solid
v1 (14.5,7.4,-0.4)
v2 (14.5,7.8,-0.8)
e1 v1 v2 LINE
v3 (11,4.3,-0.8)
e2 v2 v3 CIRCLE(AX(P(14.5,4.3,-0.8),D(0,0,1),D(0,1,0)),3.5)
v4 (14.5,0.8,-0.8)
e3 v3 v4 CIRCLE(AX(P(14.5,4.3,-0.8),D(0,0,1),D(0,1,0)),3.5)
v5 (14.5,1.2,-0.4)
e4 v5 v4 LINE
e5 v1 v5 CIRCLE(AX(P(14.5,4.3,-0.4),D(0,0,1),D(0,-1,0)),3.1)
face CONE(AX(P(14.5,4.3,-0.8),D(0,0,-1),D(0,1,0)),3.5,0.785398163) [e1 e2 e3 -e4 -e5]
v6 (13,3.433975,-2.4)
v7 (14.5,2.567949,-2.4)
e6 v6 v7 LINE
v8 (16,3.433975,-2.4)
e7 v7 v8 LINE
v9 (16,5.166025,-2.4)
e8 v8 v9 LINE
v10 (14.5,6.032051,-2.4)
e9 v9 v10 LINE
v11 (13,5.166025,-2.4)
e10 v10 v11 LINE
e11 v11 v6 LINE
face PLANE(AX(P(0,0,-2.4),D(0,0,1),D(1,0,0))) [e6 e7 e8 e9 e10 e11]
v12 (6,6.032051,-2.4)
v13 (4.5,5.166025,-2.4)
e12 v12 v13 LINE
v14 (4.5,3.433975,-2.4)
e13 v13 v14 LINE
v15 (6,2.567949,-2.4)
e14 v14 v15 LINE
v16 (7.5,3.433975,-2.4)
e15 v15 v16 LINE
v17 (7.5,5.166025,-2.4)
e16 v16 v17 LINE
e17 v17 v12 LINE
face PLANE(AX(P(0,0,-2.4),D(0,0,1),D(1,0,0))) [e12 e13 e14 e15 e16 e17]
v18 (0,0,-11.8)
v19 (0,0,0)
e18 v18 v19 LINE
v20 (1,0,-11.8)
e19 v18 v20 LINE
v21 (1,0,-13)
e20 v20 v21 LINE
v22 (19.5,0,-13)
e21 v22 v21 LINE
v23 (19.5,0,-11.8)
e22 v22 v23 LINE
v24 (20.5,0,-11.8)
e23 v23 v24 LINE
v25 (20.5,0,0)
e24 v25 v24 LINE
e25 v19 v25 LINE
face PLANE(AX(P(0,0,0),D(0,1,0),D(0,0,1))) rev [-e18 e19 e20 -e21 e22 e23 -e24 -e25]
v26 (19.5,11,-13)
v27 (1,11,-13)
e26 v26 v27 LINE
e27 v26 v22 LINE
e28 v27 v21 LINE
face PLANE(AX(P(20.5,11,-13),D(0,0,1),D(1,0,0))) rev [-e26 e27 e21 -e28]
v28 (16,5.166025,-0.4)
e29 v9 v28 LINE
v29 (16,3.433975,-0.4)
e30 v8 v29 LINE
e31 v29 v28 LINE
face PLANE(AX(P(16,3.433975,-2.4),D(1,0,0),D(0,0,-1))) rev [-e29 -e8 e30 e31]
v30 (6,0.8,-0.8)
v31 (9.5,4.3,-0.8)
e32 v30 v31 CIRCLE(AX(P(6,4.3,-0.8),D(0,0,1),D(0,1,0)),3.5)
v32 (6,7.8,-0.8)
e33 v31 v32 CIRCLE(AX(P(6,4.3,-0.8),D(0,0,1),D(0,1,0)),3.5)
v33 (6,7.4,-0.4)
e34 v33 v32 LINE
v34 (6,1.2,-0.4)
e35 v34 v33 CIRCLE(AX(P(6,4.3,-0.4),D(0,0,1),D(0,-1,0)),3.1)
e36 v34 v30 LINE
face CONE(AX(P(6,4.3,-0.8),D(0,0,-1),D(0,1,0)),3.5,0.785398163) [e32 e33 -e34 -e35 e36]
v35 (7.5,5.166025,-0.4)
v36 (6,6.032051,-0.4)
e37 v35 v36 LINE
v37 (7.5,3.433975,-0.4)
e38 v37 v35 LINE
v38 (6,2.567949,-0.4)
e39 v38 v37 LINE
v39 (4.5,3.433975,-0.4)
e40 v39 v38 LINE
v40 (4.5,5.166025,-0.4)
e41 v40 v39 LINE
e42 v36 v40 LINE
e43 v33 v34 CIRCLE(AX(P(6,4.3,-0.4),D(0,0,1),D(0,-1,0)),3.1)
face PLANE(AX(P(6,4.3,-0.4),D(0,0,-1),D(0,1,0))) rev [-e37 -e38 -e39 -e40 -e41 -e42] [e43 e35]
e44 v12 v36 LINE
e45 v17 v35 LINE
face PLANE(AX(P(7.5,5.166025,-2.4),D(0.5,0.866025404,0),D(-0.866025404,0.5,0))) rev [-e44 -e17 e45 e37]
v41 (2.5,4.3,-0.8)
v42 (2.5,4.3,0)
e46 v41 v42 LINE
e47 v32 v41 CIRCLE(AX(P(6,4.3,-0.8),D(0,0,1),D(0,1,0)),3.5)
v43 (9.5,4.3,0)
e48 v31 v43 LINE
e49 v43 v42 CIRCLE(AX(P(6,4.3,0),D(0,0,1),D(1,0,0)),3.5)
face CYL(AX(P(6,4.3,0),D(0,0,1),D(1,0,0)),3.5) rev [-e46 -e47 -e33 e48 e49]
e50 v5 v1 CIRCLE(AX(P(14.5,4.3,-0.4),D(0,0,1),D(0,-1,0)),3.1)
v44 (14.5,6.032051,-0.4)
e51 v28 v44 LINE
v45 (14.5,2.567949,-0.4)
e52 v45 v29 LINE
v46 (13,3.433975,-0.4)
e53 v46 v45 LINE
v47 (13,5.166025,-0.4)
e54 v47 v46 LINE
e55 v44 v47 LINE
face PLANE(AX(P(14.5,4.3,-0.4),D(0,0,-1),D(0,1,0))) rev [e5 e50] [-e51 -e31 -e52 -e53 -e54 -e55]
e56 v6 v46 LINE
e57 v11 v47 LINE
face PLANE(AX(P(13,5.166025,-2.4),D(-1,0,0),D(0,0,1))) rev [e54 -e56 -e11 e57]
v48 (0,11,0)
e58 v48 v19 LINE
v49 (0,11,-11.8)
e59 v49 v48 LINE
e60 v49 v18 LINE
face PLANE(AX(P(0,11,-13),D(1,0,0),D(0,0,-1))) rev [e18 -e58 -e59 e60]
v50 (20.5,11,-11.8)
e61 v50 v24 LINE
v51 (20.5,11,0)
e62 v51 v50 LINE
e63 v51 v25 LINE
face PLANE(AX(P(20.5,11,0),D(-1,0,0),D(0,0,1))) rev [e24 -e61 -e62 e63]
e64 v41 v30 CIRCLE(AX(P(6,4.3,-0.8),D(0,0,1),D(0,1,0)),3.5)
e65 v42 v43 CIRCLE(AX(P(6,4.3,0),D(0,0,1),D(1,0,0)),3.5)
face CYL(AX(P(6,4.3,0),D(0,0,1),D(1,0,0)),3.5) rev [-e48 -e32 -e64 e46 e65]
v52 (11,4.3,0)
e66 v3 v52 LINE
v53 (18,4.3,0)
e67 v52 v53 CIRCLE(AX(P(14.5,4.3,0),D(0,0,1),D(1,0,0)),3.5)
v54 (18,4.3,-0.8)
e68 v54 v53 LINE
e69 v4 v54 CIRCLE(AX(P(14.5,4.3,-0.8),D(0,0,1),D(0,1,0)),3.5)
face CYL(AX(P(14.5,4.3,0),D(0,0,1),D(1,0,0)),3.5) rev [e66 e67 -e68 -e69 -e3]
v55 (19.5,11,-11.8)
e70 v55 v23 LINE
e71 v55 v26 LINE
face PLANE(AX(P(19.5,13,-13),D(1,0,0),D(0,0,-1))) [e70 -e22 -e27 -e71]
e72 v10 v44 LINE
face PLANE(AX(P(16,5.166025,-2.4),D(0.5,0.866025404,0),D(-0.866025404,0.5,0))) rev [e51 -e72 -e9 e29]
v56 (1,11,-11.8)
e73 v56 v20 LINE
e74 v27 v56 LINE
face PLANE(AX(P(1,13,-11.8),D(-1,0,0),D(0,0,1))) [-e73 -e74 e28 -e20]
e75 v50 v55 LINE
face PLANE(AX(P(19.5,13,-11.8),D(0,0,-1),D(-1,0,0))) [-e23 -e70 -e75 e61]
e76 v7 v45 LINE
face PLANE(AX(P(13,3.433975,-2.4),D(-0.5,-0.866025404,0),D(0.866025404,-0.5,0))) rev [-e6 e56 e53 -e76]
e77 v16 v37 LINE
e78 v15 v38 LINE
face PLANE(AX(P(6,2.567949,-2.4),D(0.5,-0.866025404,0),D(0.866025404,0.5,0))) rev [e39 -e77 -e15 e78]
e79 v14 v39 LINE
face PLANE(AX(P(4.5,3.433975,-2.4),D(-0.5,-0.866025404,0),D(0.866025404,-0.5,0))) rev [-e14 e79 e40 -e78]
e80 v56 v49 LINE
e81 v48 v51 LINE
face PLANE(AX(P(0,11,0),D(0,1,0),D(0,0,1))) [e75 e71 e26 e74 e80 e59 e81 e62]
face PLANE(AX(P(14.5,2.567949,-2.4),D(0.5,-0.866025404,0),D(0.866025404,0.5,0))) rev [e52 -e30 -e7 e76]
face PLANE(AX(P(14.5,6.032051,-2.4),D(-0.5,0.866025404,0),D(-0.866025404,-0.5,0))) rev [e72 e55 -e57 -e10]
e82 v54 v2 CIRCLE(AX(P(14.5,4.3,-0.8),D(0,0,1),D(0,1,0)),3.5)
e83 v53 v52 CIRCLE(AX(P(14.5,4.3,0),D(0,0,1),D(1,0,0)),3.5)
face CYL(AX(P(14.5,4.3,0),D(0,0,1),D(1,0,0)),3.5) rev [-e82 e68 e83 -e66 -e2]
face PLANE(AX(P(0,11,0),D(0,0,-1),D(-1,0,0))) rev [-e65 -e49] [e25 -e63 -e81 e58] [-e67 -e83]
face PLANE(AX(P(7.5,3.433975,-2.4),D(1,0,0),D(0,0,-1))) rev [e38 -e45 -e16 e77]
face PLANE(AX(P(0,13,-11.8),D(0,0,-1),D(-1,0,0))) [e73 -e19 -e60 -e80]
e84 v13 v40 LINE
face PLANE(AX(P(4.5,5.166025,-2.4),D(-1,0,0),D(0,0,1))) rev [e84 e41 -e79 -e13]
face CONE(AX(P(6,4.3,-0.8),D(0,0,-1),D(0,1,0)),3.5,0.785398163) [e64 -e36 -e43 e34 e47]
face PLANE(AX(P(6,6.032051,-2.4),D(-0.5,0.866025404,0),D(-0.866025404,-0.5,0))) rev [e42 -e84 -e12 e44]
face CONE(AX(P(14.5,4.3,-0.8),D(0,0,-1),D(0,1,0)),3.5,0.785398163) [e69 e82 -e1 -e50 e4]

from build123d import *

# Parameters (mm, degrees)
SKETCH_1_W          = 20.5
SKETCH_1_H          = 13
EXTRUDE_1_DEPTH     = 11
CUT_EXTRUDE_1_DEPTH = 13
HOLE_WIZARD_1_D     = 7
HOLE_WIZARD_1_DEPTH = 4.4
HOLE_WIZARD_2_D     = 7
HOLE_WIZARD_2_DEPTH = 4.4
CUT_EXTRUDE_2_DEPTH = 2
CUT_EXTRUDE_3_DEPTH = 2


with BuildPart() as part:
    # 草图1 → 凸台-拉伸1 (new body)
    with BuildSketch(Plane(origin=(0, 0, 0), x_dir=(1, 0, 0), z_dir=(0, 1, 0))):
        with Locations((10.25, 6.5)):
            Rectangle(SKETCH_1_W, SKETCH_1_H)
    extrude(amount=EXTRUDE_1_DEPTH)

    # 草图2 → 切除-拉伸1 (cut)
    with BuildSketch(Plane(origin=(0, 0, 0), x_dir=(1, 0, 0), z_dir=(0, 1, 0))):
        Polygon((0, 11.8), (1, 11.8), (1, 13), (19.5, 13), (19.5, 11.8), (20.5, 11.8), (20.5, 26), (0, 26), align=None)
    extrude(amount=CUT_EXTRUDE_1_DEPTH, mode=Mode.SUBTRACT)

    # 孔1
    with Locations(Plane.XY):
        with Locations((6, 4.3)):
            Hole(HOLE_WIZARD_1_D / 2, depth=HOLE_WIZARD_1_DEPTH)

    # 孔2
    with Locations(Plane.XY):
        with Locations((14.5, 4.3)):
            Hole(HOLE_WIZARD_2_D / 2, depth=HOLE_WIZARD_2_DEPTH)

    # 草图7 → 旋转1 (revolve)
    with BuildSketch(Plane(origin=(6, 0, 0), x_dir=(0, 0, -1), z_dir=(1, 0, 0)), mode=Mode.PRIVATE) as revolve_1_sk:
        Polygon((0.4, 4.3), (0.4, 7.4), (0.8, 7.8), (4.4, 7.8), (4.4, 4.3), align=None)
    revolve(revolve_1_sk.sketch.rotate(Axis((6, 4.3, -4.4), (0, 0, 1)), 270), axis=Axis((6, 4.3, -4.4), (0, 0, 1)))

    # 草图8 → 旋转2 (revolve)
    with BuildSketch(Plane(origin=(14.5, 0, 0), x_dir=(0, 0, -1), z_dir=(1, 0, 0)), mode=Mode.PRIVATE) as revolve_2_sk:
        Polygon((0.4, 4.3), (0.4, 7.4), (0.8, 7.8), (4.4, 7.8), (4.4, 4.3), align=None)
    revolve(revolve_2_sk.sketch.rotate(Axis((14.5, 4.3, -4.4), (0, 0, 1)), 270), axis=Axis((14.5, 4.3, -4.4), (0, 0, 1)))

    # 草图9 → 切除-拉伸2 (cut)
    with BuildSketch(Plane.XY.offset(-0.4)):
        Polygon((4.5, 5.166025404), (4.5, 3.433974596), (6, 2.567949192), (7.5, 3.433974596), (7.5, 5.166025404), (6, 6.032050808), align=None)
    extrude(amount=-CUT_EXTRUDE_2_DEPTH, mode=Mode.SUBTRACT)

    # 草图10 → 切除-拉伸3 (cut)
    with BuildSketch(Plane.XY.offset(-0.4)):
        Polygon((13, 3.433974596), (14.5, 2.567949192), (16, 3.433974596), (16, 5.166025404), (14.5, 6.032050808), (13, 5.166025404), align=None)
    extrude(amount=-CUT_EXTRUDE_3_DEPTH, mode=Mode.SUBTRACT)


solid = part.part
